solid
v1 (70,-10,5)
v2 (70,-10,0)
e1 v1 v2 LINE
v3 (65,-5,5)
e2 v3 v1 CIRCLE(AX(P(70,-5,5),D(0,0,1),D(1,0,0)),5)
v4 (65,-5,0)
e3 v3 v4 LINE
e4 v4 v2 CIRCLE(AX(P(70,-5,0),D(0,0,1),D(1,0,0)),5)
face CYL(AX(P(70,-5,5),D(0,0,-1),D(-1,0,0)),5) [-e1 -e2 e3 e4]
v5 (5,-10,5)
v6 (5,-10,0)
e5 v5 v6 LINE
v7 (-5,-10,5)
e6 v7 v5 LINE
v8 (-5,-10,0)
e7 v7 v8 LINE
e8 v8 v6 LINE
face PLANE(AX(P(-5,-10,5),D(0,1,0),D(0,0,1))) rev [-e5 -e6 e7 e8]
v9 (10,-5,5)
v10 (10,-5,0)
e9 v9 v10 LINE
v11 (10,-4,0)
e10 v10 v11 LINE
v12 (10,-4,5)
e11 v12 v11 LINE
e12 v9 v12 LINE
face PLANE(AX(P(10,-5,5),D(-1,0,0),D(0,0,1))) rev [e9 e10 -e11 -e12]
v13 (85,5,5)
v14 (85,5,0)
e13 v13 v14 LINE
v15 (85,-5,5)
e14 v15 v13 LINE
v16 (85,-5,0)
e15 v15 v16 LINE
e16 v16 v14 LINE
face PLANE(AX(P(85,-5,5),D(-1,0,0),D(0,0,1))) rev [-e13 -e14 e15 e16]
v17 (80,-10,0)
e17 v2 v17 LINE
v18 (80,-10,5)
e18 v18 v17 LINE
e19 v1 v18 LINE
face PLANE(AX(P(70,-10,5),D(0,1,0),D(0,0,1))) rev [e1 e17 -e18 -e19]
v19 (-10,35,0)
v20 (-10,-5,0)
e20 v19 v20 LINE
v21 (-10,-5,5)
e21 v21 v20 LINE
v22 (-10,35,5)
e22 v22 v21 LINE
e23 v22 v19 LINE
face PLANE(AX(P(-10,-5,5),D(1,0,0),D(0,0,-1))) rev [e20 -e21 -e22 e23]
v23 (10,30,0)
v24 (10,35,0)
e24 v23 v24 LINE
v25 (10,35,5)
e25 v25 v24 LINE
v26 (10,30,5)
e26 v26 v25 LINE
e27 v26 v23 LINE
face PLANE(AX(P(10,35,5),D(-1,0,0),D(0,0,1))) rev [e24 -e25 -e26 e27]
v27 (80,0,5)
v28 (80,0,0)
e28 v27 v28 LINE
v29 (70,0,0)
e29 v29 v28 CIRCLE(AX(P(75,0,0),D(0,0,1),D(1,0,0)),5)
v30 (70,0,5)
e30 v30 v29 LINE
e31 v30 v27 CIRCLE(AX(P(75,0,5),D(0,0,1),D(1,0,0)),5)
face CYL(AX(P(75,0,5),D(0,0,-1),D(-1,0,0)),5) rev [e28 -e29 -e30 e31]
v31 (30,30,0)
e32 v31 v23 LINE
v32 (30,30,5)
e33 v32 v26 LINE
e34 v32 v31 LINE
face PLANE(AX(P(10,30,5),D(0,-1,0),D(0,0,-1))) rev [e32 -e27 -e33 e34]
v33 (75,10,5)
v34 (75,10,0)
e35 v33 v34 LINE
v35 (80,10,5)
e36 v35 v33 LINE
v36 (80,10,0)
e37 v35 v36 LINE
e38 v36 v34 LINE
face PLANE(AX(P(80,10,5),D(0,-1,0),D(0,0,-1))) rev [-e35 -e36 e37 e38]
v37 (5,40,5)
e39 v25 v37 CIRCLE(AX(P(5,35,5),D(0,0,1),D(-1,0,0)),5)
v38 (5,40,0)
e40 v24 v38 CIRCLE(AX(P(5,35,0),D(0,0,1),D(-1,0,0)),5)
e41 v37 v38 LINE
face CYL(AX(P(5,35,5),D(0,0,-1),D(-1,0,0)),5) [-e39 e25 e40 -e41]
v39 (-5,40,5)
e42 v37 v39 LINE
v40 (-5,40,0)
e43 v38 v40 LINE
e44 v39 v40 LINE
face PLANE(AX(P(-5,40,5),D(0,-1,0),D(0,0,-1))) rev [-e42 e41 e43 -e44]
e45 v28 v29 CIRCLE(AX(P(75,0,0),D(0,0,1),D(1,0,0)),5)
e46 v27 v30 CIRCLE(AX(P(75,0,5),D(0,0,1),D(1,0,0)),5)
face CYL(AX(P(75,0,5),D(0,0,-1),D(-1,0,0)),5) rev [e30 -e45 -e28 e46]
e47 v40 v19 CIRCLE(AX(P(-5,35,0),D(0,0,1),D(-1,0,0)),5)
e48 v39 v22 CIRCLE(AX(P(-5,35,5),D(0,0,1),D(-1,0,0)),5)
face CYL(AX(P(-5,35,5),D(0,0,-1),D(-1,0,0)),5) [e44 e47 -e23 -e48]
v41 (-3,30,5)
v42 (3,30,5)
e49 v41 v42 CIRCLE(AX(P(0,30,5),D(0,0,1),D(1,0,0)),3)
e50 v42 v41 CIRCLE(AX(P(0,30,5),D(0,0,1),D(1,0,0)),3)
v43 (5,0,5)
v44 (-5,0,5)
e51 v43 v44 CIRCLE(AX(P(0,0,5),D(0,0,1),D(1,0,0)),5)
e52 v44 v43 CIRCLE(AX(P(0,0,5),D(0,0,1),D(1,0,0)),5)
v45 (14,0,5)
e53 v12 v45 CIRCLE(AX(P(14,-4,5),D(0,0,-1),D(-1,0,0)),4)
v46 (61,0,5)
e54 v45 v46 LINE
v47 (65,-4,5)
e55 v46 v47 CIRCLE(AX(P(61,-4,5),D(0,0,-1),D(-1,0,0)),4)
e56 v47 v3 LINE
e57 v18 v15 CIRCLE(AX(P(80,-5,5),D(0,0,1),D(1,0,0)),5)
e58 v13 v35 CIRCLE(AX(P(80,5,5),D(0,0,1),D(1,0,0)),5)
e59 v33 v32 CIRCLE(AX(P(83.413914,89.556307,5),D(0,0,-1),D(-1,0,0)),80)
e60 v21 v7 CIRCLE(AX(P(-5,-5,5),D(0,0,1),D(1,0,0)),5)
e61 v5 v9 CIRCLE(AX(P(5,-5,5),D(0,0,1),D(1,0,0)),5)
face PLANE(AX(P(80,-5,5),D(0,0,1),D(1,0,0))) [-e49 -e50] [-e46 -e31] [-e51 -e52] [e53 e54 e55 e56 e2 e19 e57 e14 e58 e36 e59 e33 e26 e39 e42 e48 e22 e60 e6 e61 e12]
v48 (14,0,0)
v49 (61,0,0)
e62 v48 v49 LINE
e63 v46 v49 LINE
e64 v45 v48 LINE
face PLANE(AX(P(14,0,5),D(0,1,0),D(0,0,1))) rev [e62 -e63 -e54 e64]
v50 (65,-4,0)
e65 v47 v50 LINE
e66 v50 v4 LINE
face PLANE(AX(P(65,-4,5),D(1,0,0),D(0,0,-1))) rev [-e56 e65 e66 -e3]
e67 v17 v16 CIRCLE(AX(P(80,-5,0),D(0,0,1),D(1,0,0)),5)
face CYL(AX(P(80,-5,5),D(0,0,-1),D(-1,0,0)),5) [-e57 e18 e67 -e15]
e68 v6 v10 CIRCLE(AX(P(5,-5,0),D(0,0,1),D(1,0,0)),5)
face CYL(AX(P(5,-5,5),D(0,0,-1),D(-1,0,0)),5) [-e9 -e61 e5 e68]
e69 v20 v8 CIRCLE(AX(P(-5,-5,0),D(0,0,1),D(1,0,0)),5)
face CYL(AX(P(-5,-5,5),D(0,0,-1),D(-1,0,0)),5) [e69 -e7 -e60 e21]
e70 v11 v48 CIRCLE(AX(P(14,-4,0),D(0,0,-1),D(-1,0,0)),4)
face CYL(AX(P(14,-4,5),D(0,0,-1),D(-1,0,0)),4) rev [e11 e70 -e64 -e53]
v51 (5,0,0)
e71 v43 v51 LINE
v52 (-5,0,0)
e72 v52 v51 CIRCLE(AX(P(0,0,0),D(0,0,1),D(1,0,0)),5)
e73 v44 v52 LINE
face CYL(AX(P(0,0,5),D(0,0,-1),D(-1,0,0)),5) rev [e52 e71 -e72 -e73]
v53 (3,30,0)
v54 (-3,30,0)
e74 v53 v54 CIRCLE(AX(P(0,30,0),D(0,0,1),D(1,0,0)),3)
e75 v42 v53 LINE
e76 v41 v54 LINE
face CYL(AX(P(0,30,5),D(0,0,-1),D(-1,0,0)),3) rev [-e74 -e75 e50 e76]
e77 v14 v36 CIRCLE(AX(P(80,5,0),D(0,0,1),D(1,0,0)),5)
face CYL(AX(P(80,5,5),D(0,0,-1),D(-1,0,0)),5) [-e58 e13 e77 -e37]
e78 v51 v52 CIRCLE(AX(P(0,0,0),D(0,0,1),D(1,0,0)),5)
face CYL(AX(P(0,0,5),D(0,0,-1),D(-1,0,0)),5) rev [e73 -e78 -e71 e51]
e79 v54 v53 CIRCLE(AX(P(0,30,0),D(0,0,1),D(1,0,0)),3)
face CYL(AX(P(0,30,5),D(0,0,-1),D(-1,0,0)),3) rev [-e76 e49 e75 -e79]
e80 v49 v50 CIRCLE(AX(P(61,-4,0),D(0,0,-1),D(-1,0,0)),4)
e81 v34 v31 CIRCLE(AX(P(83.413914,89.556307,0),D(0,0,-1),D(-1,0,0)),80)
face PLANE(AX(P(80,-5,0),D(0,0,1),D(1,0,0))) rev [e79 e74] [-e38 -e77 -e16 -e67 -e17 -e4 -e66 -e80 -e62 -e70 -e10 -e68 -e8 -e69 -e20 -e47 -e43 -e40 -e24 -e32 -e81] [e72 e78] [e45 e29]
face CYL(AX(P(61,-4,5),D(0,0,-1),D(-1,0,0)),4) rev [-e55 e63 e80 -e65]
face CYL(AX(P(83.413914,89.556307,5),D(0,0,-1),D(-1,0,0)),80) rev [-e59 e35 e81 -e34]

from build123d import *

# Parameters (mm, degrees)
CARRIAGE_PLATE_PROFILE_R   = 5
CARRIAGE_PLATE_PROFILE_R_2 = 3
CARRIAGE_PLATE_5MM_DEPTH   = 5


with BuildPart() as part:
    # Carriage Plate Profile → Carriage Plate 5mm (new body)
    with BuildSketch(Plane.XY):
        with BuildLine():
            Line((-10, -5), (-10, 35))
            ThreePointArc((-10, 35), (-8.535533906, 38.535533906), (-5, 40))
            Line((-5, 40), (5, 40))
            ThreePointArc((5, 40), (8.535533906, 38.535533906), (10, 35))
            Line((10, 35), (10, 30))
            Line((10, 30), (30, 30))
            ThreePointArc((30, 30), (50.922837109, 16.451383494), (75, 10))
            Line((75, 10), (80, 10))
            ThreePointArc((80, 10), (83.535533906, 8.535533906), (85, 5))
            Line((85, 5), (85, -5))
            ThreePointArc((85, -5), (83.535533906, -8.535533906), (80, -10))
            Line((80, -10), (75, -10))
            Line((75, -10), (70, -10))
            ThreePointArc((70, -10), (66.464466094, -8.535533906), (65, -5))
            Line((65, -5), (65, -4))
            ThreePointArc((65, -4), (63.828427125, -1.171572875), (61, 0))
            Line((61, 0), (14, 0))
            ThreePointArc((14, 0), (11.171572875, -1.171572875), (10, -4))
            Line((10, -4), (10, -5))
            ThreePointArc((10, -5), (8.535533906, -8.535533906), (5, -10))
            Line((5, -10), (-5, -10))
            ThreePointArc((-5, -10), (-8.535533906, -8.535533906), (-10, -5))
        make_face()
        Circle(CARRIAGE_PLATE_PROFILE_R, mode=Mode.SUBTRACT)
        with Locations((75, 0)):
            Circle(CARRIAGE_PLATE_PROFILE_R, mode=Mode.SUBTRACT)
        with Locations((0, 30)):
            Circle(CARRIAGE_PLATE_PROFILE_R_2, mode=Mode.SUBTRACT)
    extrude(amount=CARRIAGE_PLATE_5MM_DEPTH)


solid = part.part
